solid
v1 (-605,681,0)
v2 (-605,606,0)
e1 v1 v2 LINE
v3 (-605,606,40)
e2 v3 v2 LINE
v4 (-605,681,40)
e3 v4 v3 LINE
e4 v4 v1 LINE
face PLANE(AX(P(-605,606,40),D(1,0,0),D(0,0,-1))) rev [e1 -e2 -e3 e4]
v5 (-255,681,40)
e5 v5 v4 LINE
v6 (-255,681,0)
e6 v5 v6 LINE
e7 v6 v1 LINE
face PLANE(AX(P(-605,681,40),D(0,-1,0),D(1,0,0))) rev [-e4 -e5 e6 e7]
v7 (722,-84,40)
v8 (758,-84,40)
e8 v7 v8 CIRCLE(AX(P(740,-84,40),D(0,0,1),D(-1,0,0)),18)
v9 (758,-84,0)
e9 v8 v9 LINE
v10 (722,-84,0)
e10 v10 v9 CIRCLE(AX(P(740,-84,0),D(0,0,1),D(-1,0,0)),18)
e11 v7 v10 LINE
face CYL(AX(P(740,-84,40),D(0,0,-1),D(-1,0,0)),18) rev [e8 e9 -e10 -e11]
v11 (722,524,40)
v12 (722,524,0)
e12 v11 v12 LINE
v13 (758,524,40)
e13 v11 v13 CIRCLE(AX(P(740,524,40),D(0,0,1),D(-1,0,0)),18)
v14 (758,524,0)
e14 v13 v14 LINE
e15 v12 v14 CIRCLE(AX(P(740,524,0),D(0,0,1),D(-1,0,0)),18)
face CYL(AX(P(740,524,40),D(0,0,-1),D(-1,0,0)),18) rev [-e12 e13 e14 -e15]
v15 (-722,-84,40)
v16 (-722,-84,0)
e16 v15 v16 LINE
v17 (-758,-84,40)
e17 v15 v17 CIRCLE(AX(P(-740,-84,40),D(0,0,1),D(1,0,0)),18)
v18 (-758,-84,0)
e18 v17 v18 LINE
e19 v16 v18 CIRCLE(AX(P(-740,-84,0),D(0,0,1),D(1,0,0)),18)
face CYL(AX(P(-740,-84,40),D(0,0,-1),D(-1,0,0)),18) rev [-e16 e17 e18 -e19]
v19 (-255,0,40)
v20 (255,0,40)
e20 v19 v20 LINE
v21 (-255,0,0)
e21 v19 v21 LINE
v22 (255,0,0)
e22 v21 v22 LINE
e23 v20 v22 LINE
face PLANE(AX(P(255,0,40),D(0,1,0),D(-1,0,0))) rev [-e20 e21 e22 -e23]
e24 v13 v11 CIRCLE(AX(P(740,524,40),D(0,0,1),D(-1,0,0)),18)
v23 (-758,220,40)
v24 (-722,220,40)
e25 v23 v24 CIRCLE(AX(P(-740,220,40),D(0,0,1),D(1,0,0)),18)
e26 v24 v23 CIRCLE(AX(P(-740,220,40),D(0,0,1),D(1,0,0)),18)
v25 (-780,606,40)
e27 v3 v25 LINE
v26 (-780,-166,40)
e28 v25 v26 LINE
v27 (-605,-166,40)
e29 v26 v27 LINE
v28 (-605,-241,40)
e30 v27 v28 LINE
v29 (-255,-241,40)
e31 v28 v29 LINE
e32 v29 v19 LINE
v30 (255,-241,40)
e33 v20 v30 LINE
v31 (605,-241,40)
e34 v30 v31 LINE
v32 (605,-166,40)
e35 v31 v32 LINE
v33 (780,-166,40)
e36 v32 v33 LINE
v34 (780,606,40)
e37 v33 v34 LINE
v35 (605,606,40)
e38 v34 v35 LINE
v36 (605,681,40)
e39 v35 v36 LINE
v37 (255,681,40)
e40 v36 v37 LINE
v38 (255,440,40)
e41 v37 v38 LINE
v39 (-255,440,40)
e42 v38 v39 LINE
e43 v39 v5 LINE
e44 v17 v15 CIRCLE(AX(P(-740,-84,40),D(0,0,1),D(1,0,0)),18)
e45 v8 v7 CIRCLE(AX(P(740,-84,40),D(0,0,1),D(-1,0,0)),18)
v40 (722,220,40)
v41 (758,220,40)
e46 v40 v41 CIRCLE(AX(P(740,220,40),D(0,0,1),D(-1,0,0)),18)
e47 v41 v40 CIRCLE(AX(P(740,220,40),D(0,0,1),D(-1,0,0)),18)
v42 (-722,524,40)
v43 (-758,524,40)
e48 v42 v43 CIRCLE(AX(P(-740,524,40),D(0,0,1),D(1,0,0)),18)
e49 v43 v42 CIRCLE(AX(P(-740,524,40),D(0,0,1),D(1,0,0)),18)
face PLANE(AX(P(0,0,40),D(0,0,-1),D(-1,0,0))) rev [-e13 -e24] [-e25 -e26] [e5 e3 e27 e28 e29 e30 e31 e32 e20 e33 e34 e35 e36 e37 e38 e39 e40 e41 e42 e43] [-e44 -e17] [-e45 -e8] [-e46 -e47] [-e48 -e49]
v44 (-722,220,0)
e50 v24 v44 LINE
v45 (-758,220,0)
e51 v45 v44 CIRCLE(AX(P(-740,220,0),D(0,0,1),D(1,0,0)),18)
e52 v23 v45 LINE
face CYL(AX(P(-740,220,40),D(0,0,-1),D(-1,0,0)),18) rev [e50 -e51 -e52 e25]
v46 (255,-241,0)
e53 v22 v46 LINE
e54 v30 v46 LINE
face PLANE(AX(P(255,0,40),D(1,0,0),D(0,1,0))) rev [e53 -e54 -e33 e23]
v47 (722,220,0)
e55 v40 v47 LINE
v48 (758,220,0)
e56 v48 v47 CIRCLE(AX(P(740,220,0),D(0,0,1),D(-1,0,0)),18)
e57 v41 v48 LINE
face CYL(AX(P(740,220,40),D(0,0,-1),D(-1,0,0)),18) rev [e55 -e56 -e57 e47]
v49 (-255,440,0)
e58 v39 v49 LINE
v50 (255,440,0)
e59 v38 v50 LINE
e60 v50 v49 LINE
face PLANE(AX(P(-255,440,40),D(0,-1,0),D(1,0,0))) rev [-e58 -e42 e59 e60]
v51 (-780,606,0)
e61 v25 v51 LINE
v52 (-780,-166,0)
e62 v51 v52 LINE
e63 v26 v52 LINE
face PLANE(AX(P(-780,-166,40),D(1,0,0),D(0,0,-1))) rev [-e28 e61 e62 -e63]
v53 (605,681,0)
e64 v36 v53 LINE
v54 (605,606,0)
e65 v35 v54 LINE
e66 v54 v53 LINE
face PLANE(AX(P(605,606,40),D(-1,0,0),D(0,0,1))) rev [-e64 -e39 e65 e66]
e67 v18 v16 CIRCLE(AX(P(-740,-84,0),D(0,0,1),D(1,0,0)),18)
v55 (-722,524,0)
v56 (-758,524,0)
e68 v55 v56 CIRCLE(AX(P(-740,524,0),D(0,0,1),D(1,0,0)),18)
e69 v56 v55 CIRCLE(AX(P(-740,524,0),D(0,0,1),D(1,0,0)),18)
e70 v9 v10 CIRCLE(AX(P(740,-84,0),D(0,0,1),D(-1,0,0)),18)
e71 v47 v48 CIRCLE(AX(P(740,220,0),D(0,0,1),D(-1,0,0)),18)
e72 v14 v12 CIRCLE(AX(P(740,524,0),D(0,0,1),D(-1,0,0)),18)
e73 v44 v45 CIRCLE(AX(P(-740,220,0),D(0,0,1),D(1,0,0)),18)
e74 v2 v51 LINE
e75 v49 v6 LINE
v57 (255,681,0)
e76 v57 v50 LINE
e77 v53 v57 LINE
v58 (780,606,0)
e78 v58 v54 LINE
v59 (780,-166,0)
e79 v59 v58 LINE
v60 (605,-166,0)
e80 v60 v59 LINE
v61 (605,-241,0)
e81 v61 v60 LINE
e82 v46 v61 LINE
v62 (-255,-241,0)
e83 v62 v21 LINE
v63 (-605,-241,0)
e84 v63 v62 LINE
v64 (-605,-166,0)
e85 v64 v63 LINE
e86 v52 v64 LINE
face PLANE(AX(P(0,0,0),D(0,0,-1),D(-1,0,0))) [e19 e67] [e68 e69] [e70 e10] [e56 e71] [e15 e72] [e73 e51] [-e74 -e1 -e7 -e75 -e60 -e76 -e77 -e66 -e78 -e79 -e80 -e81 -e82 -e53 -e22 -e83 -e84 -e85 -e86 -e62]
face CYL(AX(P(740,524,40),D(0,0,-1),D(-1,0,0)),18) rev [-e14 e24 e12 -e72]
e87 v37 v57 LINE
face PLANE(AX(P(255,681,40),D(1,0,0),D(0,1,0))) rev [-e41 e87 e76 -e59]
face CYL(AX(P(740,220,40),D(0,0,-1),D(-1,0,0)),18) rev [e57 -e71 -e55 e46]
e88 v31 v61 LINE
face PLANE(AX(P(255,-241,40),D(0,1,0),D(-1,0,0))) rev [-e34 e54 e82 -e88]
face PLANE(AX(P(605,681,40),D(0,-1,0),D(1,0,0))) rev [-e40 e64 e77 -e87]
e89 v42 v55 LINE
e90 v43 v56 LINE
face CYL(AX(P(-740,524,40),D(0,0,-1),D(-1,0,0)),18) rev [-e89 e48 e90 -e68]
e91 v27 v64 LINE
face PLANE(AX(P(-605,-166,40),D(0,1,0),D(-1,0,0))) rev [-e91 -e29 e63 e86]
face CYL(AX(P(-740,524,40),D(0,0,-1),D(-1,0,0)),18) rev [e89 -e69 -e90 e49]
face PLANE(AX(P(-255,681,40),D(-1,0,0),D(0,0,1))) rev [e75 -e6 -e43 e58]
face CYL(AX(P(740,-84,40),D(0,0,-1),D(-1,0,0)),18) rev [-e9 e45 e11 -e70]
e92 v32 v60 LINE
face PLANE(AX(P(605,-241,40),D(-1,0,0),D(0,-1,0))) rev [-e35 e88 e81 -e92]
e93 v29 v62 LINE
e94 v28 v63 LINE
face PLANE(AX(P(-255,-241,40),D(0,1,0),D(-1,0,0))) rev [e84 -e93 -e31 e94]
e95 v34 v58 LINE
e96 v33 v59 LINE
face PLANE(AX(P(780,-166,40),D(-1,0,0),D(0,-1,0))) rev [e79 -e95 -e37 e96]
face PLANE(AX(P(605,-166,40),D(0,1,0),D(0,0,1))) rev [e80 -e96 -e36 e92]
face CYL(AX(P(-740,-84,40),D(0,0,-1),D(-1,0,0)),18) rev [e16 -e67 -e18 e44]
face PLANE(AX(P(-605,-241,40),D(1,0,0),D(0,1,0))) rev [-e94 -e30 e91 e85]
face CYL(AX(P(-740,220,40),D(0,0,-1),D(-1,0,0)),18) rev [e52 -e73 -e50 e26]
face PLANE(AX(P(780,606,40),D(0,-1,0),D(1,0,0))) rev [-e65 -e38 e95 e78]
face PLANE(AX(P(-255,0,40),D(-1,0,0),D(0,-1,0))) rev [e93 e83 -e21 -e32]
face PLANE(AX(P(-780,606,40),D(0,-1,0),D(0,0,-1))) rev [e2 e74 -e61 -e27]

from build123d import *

# Parameters (mm, degrees)
SKETCH1_R           = 18
BOSS_EXTRUDE1_DEPTH = 40


with BuildPart() as part:
    # Sketch1 → Boss-Extrude1 (new body)
    with BuildSketch(Plane.XY):
        Polygon((255, 0), (-255, 0), (-255, -241), (-605, -241), (-605, -166), (-780, -166), (-780, 606), (-605, 606), (-605, 681), (-255, 681), (-255, 440), (255, 440), (255, 681), (605, 681), (605, 606), (780, 606), (780, -166), (605, -166), (605, -241), (255, -241), align=None)
        with Locations((-740, 524)):
            Circle(SKETCH1_R, mode=Mode.SUBTRACT)
        with Locations((-740, 220)):
            Circle(SKETCH1_R, mode=Mode.SUBTRACT)
        with Locations((-740, -84)):
            Circle(SKETCH1_R, mode=Mode.SUBTRACT)
        with Locations(Location((740, 220, 0), (0, 0, 180))):
            Circle(SKETCH1_R, mode=Mode.SUBTRACT)
        with Locations(Location((740, 524, 0), (0, 0, 180))):
            Circle(SKETCH1_R, mode=Mode.SUBTRACT)
        with Locations(Location((740, -84, 0), (0, 0, 180))):
            Circle(SKETCH1_R, mode=Mode.SUBTRACT)
    extrude(amount=BOSS_EXTRUDE1_DEPTH)


solid = part.part
